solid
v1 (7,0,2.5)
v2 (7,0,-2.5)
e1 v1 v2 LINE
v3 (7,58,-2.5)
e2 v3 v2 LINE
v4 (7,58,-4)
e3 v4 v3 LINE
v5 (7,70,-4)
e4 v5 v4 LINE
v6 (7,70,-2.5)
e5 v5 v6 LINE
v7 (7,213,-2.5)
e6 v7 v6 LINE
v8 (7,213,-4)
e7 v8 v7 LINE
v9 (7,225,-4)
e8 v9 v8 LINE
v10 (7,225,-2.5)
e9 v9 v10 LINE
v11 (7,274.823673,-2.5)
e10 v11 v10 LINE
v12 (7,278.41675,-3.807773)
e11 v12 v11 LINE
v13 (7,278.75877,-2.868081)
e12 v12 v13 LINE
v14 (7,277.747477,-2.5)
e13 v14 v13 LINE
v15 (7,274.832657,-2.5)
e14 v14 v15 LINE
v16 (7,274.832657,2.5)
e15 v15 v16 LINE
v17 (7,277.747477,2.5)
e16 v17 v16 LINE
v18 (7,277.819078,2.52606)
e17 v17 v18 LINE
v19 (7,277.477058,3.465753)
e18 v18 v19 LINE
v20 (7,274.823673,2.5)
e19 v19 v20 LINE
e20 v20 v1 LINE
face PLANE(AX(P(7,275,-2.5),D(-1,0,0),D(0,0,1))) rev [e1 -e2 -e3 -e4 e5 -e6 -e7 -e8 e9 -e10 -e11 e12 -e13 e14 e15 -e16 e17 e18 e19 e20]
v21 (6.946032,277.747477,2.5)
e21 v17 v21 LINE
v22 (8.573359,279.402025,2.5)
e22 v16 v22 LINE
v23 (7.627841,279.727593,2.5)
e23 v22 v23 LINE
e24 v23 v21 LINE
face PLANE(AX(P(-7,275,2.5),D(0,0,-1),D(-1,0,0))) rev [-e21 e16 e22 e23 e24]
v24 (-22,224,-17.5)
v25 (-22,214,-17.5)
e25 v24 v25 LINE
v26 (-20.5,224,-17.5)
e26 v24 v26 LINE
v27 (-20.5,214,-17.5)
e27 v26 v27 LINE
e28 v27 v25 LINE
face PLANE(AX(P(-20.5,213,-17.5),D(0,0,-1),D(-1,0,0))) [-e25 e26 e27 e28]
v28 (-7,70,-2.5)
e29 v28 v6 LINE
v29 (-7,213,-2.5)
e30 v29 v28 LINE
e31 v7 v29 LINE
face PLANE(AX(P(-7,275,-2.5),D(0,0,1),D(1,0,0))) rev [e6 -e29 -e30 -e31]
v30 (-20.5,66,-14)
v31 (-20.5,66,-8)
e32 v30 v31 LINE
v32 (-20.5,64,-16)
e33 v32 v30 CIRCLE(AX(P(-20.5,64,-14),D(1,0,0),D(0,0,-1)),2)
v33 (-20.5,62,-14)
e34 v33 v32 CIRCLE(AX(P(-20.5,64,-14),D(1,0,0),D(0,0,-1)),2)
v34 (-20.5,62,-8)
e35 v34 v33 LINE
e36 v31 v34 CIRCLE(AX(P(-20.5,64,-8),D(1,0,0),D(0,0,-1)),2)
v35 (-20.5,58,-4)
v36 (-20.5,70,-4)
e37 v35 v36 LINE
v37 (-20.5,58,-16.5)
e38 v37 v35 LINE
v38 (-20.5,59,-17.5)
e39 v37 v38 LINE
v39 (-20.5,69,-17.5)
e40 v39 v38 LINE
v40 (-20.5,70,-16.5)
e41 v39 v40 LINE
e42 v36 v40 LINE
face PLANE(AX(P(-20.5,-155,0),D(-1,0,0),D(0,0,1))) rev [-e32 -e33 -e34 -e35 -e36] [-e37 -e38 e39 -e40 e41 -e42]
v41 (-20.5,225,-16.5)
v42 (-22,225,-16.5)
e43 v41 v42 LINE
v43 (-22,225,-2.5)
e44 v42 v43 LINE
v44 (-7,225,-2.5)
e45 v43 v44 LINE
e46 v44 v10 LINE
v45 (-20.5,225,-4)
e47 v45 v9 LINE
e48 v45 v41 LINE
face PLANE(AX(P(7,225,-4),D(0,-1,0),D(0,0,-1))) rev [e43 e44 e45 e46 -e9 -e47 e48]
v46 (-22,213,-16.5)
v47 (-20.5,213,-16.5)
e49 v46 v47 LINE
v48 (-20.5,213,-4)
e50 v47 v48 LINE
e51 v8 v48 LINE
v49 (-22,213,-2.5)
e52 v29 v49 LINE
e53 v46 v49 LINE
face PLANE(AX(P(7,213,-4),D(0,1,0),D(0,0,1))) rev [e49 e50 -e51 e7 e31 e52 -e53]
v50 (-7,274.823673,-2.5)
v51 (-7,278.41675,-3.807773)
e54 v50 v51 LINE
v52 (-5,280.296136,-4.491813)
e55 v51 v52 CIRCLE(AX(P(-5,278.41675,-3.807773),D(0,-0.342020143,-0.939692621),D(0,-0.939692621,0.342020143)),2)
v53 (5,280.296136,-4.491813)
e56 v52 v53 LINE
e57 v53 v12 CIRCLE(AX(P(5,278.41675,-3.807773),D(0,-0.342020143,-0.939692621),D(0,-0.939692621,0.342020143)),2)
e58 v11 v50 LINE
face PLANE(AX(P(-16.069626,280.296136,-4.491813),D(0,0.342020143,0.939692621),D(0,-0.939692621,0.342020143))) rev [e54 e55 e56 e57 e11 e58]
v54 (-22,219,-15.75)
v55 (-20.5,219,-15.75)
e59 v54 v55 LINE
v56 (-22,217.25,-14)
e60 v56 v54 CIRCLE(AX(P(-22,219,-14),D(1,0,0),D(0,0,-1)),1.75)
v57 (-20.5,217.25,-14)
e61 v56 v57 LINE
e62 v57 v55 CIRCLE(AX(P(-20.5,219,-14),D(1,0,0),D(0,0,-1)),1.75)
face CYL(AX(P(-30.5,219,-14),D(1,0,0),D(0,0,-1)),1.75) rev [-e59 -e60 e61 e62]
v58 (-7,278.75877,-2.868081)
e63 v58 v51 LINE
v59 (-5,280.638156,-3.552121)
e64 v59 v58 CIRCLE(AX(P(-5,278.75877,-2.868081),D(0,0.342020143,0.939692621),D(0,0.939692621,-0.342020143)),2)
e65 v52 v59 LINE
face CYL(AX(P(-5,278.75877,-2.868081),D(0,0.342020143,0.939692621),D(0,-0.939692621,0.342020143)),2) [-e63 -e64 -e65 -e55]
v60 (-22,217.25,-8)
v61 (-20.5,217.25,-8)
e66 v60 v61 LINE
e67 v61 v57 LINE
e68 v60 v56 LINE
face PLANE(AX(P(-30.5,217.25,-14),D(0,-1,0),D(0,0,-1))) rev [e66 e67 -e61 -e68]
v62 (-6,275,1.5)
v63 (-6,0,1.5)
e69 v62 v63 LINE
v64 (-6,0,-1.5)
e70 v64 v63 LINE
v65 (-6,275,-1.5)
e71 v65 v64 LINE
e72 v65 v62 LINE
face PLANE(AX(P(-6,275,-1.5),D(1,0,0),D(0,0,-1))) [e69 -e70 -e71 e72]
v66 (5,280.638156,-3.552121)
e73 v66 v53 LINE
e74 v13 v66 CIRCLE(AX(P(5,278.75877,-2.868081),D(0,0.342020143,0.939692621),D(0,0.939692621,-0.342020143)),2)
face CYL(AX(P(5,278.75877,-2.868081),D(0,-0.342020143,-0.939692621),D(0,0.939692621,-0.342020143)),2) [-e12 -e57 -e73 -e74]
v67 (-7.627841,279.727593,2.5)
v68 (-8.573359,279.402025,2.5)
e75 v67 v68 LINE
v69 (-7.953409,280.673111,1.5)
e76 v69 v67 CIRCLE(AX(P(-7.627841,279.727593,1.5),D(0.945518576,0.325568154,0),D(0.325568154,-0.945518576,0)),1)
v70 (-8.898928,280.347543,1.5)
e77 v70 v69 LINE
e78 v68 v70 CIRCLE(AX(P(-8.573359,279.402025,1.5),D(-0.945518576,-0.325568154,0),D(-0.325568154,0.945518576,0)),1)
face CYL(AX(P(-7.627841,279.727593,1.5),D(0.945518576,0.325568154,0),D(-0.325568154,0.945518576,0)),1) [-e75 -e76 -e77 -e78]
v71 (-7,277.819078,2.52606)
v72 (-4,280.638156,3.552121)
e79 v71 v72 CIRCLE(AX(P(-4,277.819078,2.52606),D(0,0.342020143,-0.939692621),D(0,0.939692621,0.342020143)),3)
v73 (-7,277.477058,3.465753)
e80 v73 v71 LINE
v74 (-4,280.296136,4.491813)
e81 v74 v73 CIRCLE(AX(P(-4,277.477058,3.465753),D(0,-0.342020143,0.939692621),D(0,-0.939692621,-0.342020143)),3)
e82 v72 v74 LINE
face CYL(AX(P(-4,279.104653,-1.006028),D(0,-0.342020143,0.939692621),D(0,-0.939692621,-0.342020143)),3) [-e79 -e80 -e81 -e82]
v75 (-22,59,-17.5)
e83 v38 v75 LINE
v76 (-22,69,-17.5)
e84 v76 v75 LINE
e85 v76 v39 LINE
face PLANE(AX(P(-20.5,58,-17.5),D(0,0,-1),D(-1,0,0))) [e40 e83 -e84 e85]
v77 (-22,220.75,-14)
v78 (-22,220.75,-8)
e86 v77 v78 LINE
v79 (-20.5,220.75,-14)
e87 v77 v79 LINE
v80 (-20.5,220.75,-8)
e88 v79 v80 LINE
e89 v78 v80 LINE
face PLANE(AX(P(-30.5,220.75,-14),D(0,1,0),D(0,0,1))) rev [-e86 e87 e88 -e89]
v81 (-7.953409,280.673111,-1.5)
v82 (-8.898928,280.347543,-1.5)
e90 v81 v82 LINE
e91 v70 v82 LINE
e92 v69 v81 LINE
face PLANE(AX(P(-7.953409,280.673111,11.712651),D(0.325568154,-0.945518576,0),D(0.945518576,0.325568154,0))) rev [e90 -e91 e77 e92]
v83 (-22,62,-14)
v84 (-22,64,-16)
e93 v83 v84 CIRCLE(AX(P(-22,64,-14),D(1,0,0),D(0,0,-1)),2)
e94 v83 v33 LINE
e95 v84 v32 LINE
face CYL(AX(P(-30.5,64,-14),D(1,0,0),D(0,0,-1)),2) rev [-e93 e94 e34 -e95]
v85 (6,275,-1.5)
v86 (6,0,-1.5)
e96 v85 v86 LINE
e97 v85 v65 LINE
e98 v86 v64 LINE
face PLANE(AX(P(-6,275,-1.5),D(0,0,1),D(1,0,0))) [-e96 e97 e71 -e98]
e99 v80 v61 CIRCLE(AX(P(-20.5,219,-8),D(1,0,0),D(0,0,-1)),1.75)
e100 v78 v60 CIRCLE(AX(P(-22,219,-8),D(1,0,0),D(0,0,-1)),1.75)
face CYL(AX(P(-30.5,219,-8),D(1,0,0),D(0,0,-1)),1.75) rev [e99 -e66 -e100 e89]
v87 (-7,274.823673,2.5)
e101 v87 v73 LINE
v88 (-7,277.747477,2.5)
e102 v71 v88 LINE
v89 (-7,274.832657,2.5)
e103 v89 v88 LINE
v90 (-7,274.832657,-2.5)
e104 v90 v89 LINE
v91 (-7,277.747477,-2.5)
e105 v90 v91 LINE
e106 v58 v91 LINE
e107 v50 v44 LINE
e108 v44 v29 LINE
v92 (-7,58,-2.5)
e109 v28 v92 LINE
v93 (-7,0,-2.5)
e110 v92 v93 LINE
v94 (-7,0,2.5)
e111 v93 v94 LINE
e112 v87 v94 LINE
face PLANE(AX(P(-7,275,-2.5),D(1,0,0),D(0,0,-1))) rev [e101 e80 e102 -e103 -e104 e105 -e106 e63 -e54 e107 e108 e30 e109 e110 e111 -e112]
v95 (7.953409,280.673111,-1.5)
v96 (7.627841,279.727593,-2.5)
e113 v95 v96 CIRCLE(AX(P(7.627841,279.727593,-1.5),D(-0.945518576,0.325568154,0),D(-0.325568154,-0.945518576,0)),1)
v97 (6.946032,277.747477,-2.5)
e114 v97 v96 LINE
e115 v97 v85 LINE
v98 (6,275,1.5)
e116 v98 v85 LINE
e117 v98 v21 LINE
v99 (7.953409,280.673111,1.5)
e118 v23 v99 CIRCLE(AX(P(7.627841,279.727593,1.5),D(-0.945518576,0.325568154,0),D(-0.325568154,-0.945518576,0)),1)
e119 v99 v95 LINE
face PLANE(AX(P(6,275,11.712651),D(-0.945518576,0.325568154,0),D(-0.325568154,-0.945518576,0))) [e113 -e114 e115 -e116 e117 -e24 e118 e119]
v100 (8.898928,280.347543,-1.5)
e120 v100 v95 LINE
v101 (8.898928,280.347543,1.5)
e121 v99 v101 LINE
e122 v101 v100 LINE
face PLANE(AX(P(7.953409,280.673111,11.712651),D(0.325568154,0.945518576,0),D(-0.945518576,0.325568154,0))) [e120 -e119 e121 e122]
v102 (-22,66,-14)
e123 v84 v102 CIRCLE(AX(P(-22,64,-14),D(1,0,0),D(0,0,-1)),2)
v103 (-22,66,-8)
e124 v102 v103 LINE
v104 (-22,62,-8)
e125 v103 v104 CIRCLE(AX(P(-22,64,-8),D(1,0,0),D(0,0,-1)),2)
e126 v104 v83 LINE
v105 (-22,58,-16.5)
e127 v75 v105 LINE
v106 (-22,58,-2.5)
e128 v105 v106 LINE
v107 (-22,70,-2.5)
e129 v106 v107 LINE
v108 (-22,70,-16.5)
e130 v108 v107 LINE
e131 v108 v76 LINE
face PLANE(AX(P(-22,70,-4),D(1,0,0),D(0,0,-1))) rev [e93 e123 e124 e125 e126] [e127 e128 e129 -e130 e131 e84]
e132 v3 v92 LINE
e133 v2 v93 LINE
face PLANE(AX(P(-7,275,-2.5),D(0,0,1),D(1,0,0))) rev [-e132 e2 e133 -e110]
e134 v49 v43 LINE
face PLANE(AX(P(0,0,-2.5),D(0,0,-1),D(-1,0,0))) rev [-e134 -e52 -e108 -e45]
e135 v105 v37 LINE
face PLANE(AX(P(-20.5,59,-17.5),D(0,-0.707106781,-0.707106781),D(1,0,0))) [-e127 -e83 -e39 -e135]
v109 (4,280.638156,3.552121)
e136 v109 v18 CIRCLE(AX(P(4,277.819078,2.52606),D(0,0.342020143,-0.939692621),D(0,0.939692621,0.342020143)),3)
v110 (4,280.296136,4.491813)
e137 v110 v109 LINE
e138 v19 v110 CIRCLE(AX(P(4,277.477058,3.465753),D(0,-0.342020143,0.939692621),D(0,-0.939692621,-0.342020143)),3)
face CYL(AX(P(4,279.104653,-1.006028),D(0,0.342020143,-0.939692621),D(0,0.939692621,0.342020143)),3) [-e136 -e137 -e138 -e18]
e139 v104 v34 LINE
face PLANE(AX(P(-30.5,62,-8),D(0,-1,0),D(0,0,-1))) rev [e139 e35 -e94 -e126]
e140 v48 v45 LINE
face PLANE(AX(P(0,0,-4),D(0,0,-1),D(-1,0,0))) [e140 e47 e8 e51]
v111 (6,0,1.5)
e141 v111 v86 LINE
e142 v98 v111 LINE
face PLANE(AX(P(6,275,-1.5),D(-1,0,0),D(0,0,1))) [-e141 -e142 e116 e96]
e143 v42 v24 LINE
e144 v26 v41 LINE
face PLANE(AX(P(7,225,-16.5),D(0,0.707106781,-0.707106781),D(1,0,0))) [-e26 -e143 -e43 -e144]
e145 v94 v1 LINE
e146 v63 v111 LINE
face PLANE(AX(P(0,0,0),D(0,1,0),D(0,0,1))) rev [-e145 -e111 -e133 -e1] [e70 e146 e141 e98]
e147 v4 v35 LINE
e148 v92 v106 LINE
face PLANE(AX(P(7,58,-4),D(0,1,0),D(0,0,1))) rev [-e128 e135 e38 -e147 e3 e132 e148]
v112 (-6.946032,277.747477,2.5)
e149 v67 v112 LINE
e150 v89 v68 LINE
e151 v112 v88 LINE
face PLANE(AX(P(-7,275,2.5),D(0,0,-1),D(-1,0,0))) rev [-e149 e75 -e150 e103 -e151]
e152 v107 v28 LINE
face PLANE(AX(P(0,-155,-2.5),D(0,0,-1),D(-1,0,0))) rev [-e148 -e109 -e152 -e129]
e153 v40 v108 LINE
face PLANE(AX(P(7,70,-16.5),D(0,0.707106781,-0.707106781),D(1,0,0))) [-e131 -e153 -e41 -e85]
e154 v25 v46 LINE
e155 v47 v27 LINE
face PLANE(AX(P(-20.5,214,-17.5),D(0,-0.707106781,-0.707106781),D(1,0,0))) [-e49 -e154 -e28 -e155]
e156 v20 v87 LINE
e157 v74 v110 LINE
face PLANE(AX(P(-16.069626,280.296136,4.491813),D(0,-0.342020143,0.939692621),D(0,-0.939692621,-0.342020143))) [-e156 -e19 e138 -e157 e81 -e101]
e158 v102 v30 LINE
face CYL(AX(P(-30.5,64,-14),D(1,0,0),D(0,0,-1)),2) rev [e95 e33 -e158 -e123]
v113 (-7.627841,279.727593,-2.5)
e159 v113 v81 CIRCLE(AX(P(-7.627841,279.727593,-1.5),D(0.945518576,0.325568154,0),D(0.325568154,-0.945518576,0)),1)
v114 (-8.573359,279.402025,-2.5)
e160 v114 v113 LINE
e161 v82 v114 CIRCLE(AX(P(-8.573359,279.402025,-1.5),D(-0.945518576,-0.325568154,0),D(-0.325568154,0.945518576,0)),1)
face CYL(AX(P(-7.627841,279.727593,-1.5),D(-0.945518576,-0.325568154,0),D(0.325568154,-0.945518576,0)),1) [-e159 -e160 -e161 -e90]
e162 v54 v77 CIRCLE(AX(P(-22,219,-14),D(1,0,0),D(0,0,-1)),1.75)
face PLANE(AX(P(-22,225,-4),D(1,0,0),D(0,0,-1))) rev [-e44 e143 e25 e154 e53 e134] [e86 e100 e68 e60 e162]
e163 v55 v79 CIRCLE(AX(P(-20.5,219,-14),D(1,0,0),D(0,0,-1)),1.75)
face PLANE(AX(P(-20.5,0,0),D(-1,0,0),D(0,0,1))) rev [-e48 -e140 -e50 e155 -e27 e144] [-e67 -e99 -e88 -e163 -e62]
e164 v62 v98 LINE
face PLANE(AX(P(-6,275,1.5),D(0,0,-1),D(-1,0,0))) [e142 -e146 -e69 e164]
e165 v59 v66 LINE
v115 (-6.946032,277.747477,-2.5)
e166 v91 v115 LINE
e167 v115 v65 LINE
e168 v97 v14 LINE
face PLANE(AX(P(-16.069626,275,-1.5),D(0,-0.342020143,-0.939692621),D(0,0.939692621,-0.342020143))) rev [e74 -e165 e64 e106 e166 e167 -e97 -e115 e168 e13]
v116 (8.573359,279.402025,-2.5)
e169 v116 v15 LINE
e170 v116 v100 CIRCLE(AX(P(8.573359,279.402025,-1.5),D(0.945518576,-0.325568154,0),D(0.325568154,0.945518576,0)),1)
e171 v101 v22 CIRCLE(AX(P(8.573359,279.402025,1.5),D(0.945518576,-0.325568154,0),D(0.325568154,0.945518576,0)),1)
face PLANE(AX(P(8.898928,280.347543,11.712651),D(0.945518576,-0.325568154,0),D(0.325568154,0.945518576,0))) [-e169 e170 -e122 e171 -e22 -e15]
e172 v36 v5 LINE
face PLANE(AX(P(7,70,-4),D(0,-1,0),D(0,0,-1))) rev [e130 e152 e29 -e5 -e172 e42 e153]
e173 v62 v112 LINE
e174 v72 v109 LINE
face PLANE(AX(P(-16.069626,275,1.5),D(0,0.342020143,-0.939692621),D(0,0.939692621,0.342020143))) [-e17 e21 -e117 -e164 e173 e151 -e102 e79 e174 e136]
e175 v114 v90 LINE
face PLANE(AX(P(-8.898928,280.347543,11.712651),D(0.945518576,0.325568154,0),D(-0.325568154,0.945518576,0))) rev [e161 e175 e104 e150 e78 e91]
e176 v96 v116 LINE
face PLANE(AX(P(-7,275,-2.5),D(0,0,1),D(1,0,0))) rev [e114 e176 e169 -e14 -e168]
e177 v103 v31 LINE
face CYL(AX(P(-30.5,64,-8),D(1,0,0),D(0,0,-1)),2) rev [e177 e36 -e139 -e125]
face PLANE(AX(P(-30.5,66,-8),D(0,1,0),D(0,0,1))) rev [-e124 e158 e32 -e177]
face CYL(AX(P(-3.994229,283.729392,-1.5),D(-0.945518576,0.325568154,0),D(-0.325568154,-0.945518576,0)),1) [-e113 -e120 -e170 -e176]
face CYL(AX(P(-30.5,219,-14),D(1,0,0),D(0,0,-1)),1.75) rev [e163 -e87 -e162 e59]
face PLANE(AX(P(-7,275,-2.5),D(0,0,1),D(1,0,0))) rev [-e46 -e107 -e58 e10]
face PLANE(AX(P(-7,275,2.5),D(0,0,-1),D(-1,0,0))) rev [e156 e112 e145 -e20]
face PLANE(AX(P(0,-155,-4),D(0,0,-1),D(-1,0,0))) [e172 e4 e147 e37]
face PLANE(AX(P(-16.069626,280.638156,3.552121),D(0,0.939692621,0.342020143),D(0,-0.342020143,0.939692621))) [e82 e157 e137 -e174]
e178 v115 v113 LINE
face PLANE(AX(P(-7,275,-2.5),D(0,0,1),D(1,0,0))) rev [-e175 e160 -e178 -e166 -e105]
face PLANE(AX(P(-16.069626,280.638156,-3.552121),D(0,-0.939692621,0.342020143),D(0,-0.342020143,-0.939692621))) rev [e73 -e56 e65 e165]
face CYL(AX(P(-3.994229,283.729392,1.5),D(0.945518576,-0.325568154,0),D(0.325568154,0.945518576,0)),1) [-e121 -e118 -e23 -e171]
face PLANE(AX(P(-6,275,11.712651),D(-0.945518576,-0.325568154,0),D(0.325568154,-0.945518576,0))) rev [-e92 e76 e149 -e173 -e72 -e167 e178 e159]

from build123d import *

# Parameters (mm, degrees)
SKETCH1_W           = 14
SKETCH1_H           = 5
SKETCH1_W_2         = 12
SKETCH1_H_2         = 3
BOSS_EXTRUDE1_DEPTH = 275
SKETCH2_W           = 29
SKETCH2_H           = 12
BOSS_EXTRUDE2_DEPTH = 1.5
SKETCH3_W           = 15
SKETCH3_H           = 12
BOSS_EXTRUDE3_DEPTH = 1.5
LPATTERN1_COUNT     = 2
LPATTERN1_PITCH     = 155
CHAMFER1_SIZE       = 1
CUT_EXTRUDE1_DEPTH  = 10
BOSS_EXTRUDE4_REACH = 279.078
FILLET1_R           = 3
BOSS_EXTRUDE5_REACH = 283.899
FILLET2_R           = 1
FILLET3_R           = 2


with BuildPart() as part:
    # Sketch1 → Boss-Extrude1 (new body)
    with BuildSketch(Plane(origin=(0, 0, 0), x_dir=(1, 0, 0), z_dir=(0, 1, 0))):
        Rectangle(SKETCH1_W, SKETCH1_H)
        Rectangle(SKETCH1_W_2, SKETCH1_H_2, mode=Mode.SUBTRACT)
    extrude(amount=BOSS_EXTRUDE1_DEPTH)

    # Sketch2 → Boss-Extrude2 (add)
    with BuildSketch(Plane(origin=(0, 0, -2.5), x_dir=(-1, 0, 0), z_dir=(0, 0, -1))):
        with Locations((7.5, 219)):
            Rectangle(SKETCH2_W, SKETCH2_H)
    boss_extrude2 = extrude(amount=BOSS_EXTRUDE2_DEPTH)

    # Sketch3 → Boss-Extrude3 (add)
    with BuildSketch(Plane.ZY.offset(22)):
        with Locations((-10, 219)):
            Rectangle(SKETCH3_W, SKETCH3_H)
    boss_extrude3 = extrude(amount=-BOSS_EXTRUDE3_DEPTH)

    # LPattern1: Boss-Extrude2, Boss-Extrude3 ×2
    with Locations(*[(0, -i * LPATTERN1_PITCH, 0) for i in range(1, LPATTERN1_COUNT)]):
        add(boss_extrude2)
        add(boss_extrude3)

    # Chamfer1
    chamfer1_edges = [part.edges().sort_by_distance(p)[0] for p in [
        (-21.25, 213, -17.5),
        (-21.25, 225, -17.5),
        (-21.25, 58, -17.5),
        (-21.25, 70, -17.5),
    ]]
    chamfer(chamfer1_edges, length=CHAMFER1_SIZE)

    # Sketch4 → Cut-Extrude1 (cut)
    with BuildSketch(Plane(origin=(-20.5, 0, 0), x_dir=(0, 0, -1), z_dir=(1, 0, 0))):
        with BuildLine():
            Line((8, 66), (14, 66))
            ThreePointArc((14, 66), (16, 64), (14, 62))
            Line((14, 62), (8, 62))
            ThreePointArc((8, 62), (6, 64), (8, 66))
        make_face()
        with BuildLine():
            Line((14, 217.25), (8, 217.25))
            ThreePointArc((8, 217.25), (6.25, 219), (8, 220.75))
            Line((8, 220.75), (14, 220.75))
            ThreePointArc((14, 220.75), (15.75, 219), (14, 217.25))
        make_face()
    extrude(amount=-CUT_EXTRUDE1_DEPTH, mode=Mode.SUBTRACT)

    # Boss-Extrude4: up to this face of the body (flat: up to its plane)
    boss_extrude4_end = Plane(part.part.faces().sort_by_distance((-7, 137.5, 0))[0])
    # Sketch5 → Boss-Extrude4 (add, up to the picked face)
    with BuildSketch(Plane(origin=(7, 0, 0), x_dir=(0, 0, -1), z_dir=(1, 0, 0)), mode=Mode.PRIVATE) as boss_extrude4_sk1:
        Polygon((-1.5, 275), (-3.55212086, 280.638155725), (-4.491813481, 280.296135581), (-1.5, 272.0761956), align=None)
    boss_extrude4_tool1 = split(extrude(boss_extrude4_sk1.sketch, amount=-BOSS_EXTRUDE4_REACH, mode=Mode.PRIVATE), bisect_by=boss_extrude4_end, keep=Keep.BOTH, mode=Mode.PRIVATE)
    boss_extrude4 = boss_extrude4_tool1.solids().sort_by(Axis((7, 276.951919, 2.775572), (-1, 0, 0)))[0]
    add(boss_extrude4)

    # Fillet1
    fillet1_edges = [part.edges().sort_by_distance(p)[0] for p in [
        (7, 280.467145653, 4.02196717),
        (-7, 280.467145653, 4.02196717),
    ]]
    fillet(fillet1_edges, radius=FILLET1_R)

    # Boss-Extrude5: up to this face of the body (flat: up to its plane)
    boss_extrude5_end = Plane(part.part.faces().sort_by_distance((0, 137.41183651, 2.5))[0])
    # Sketch6 → Boss-Extrude5 (add, up to the picked face)
    with BuildSketch(Plane(origin=(0, 0, -2.5), x_dir=(-1, 0, 0), z_dir=(0, 0, -1)), mode=Mode.PRIVATE) as boss_extrude5_sk1:
        Polygon((-6, 275), (-7.953408927, 280.673111454), (-8.898927502, 280.347543299), (-6, 271.928446513), align=None)
    boss_extrude5_tool1 = split(extrude(boss_extrude5_sk1.sketch, amount=-BOSS_EXTRUDE5_REACH, mode=Mode.PRIVATE), bisect_by=boss_extrude5_end, keep=Keep.BOTH, mode=Mode.PRIVATE)
    # Sketch6 → Boss-Extrude5 (add, up to the picked face)
    with BuildSketch(Plane(origin=(0, 0, -2.5), x_dir=(-1, 0, 0), z_dir=(0, 0, -1)), mode=Mode.PRIVATE) as boss_extrude5_sk2:
        Polygon((6, 275), (6, 271.928446513), (8.898927502, 280.347543299), (7.953408927, 280.673111454), align=None)
    boss_extrude5_tool2 = split(extrude(boss_extrude5_sk2.sketch, amount=-BOSS_EXTRUDE5_REACH, mode=Mode.PRIVATE), bisect_by=boss_extrude5_end, keep=Keep.BOTH, mode=Mode.PRIVATE)
    add(boss_extrude5_tool1.solids().sort_by(Axis((7.228438, 276.932112, -2.5), (0, 0, 1)))[0])
    add(boss_extrude5_tool2.solids().sort_by(Axis((-7.228438, 276.932112, -2.5), (0, 0, 1)))[0])

    # Fillet2
    fillet2_edges = [part.edges().sort_by_distance(p)[0] for p in [
        (8.426168215, 280.510327376, 2.5),
        (8.426168215, 280.510327376, -2.5),
        (-8.426168215, 280.510327376, 2.5),
        (-8.426168215, 280.510327376, -2.5),
    ]]
    fillet(fillet2_edges, radius=FILLET2_R)

    # Mirror1: Boss-Extrude4 across plane
    add(boss_extrude4.mirror(Plane.XY))

    # Fillet3
    fillet3_edges = [part.edges().sort_by_distance(p)[0] for p in [
        (-7, 280.467145653, -4.02196717),
        (7, 280.467145653, -4.02196717),
    ]]
    fillet(fillet3_edges, radius=FILLET3_R)


solid = part.part
